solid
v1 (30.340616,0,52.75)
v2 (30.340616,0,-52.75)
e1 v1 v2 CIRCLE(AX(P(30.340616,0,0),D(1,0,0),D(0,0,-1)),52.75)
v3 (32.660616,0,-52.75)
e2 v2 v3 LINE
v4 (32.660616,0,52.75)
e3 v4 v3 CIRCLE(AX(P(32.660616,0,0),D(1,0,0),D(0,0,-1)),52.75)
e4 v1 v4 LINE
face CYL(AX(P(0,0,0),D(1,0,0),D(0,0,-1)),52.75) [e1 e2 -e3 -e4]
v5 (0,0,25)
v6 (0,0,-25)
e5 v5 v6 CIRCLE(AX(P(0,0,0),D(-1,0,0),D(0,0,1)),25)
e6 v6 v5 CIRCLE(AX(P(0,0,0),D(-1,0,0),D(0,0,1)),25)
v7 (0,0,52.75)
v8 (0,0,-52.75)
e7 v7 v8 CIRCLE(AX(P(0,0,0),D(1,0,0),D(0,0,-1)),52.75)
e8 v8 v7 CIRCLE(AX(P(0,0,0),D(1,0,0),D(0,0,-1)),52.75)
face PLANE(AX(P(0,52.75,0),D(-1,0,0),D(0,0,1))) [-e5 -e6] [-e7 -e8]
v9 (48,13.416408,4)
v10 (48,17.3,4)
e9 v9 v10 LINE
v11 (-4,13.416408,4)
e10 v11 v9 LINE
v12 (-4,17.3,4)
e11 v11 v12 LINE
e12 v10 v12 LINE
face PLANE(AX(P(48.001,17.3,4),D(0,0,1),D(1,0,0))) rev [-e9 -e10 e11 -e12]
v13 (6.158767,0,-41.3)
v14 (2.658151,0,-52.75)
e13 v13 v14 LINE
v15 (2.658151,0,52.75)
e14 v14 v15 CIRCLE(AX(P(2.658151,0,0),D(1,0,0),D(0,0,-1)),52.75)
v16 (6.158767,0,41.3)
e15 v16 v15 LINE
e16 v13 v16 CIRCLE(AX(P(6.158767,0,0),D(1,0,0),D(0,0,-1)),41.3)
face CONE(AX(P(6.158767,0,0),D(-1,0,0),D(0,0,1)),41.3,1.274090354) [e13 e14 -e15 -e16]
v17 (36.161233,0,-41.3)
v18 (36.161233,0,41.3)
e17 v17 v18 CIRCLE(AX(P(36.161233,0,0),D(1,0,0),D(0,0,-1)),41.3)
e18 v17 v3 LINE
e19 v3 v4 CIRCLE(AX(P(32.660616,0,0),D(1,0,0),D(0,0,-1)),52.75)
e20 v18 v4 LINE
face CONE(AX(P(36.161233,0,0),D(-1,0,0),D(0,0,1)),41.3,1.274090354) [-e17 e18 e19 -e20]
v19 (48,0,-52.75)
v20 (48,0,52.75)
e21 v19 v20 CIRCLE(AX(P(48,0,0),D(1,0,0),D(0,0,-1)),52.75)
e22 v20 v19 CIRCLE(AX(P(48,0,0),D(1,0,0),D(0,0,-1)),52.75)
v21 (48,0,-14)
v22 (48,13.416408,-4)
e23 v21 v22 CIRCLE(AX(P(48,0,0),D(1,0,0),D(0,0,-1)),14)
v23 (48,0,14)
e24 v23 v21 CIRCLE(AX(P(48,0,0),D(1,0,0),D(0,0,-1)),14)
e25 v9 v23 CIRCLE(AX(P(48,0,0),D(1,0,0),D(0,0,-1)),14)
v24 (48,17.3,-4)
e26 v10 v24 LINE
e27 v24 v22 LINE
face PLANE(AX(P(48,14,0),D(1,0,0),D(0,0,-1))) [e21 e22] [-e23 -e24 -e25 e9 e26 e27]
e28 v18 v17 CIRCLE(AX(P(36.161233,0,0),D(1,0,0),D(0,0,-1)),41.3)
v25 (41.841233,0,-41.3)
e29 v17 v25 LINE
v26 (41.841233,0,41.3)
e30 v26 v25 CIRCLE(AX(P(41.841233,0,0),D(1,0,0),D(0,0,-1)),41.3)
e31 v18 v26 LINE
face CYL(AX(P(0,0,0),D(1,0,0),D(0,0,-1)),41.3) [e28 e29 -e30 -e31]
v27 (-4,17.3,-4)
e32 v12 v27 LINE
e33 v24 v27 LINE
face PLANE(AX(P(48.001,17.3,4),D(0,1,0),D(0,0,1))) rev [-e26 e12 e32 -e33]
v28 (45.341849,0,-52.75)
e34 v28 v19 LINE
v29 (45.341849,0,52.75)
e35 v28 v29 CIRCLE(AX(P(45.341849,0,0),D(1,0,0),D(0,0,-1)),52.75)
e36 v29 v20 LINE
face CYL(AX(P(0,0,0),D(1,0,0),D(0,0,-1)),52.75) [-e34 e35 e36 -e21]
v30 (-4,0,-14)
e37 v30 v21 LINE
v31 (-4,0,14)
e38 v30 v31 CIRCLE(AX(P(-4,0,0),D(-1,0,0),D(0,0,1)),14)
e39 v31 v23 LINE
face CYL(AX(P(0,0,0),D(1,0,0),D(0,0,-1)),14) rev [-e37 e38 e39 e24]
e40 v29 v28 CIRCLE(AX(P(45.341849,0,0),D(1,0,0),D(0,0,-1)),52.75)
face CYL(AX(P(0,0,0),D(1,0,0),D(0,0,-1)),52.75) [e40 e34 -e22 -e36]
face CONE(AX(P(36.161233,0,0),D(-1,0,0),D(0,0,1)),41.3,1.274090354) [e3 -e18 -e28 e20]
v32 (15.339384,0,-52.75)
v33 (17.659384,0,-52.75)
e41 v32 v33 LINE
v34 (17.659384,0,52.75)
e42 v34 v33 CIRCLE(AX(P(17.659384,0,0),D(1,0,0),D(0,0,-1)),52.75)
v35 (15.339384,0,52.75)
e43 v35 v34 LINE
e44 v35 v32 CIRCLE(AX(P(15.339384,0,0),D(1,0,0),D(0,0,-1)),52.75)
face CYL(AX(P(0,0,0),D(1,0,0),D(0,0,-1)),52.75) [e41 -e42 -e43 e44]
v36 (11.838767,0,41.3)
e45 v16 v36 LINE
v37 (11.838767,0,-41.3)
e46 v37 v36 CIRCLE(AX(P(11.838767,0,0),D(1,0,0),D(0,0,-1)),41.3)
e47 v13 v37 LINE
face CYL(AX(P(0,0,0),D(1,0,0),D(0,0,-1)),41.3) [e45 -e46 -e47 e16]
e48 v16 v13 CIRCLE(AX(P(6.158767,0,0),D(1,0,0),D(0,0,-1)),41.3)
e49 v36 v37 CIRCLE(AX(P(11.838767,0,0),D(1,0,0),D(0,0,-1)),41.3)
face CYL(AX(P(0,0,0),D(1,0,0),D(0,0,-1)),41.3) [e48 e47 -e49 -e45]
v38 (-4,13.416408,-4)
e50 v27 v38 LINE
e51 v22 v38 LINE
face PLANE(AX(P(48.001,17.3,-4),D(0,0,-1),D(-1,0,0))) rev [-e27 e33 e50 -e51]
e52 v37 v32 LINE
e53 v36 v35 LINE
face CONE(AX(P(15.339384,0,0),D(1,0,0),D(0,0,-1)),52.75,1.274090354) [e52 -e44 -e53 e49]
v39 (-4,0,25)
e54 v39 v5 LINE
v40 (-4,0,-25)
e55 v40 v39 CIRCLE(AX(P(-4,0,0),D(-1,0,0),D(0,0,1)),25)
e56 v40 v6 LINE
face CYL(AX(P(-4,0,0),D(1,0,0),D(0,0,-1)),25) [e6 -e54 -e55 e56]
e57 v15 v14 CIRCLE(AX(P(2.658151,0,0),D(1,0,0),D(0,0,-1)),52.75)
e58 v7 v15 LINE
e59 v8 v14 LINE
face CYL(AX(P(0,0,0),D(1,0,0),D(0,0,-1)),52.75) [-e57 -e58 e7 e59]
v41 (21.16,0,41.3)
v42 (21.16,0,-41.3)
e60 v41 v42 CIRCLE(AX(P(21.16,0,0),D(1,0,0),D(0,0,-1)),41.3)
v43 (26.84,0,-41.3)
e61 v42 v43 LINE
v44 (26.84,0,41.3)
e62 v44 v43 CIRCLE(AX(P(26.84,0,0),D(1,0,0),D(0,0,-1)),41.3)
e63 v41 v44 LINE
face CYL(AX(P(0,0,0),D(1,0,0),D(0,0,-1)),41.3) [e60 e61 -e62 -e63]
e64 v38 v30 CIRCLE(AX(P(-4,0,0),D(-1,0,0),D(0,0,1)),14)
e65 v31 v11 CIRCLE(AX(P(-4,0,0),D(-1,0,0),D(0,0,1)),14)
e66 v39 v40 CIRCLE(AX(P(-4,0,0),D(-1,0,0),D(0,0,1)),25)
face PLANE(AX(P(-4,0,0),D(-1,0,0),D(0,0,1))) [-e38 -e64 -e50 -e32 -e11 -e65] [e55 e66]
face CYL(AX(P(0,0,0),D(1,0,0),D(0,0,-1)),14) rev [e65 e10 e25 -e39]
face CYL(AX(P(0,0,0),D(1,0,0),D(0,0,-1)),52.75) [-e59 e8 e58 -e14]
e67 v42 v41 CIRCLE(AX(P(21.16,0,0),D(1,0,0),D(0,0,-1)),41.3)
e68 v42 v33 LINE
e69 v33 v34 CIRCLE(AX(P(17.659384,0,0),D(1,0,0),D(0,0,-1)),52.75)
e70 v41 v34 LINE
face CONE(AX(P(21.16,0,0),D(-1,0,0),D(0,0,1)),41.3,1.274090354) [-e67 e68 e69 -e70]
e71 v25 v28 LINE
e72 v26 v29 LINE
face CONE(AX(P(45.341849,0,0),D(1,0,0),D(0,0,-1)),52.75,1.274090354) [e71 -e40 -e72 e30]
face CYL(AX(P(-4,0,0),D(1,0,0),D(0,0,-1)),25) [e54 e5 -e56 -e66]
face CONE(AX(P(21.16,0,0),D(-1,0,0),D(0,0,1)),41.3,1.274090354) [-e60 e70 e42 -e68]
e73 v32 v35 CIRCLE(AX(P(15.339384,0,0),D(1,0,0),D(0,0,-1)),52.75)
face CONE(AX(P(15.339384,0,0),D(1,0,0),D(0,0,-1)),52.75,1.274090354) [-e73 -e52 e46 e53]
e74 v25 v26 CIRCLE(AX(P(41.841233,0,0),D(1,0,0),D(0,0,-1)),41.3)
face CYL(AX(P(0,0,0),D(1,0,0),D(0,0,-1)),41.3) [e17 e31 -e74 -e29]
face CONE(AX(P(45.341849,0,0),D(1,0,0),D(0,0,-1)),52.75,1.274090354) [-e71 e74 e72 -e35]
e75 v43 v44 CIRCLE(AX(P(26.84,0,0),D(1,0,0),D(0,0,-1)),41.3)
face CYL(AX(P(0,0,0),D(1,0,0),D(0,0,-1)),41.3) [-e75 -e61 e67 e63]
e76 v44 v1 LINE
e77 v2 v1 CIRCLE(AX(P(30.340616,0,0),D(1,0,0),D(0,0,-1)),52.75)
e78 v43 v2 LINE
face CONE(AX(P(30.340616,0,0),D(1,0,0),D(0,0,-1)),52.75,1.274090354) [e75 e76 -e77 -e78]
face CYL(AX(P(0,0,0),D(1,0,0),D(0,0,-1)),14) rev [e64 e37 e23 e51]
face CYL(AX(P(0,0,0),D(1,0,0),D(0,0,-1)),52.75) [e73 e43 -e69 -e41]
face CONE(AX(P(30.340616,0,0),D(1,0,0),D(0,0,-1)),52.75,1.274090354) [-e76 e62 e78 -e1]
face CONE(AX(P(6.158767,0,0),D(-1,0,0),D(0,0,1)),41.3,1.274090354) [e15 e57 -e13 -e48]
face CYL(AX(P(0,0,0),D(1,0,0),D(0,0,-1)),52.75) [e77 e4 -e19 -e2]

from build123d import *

# Parameters (mm, degrees)
SKETCH8_R           = 25
SKETCH8_R_2         = 14
BOSS_EXTRUDE2_DEPTH = 4
CUT_EXTRUDE5_REACH  = 92.935
SKETCH9_W           = 8
SKETCH9_H           = 6.6


with BuildPart() as part:
    # Sketch1 → Revolve1 (revolve)
    with BuildSketch(Plane.XY, mode=Mode.PRIVATE) as revolve1_sk:
        Polygon((6.158767395, 41.3), (2.658151092, 52.75), (0, 52.75), (0, 14), (48, 14), (48, 52.75), (45.341848908, 52.75), (41.841232605, 41.3), (36.161232605, 41.3), (32.660616303, 52.75), (30.340616303, 52.75), (26.84, 41.3), (21.16, 41.3), (17.659383697, 52.75), (15.339383697, 52.75), (11.838767395, 41.3), align=None)
    revolve(revolve1_sk.sketch.rotate(Axis((0, 0, 0), (1, 0, 0)), 270), axis=Axis((0, 0, 0), (1, 0, 0)))

    # Sketch8 → Boss-Extrude2 (add)
    with BuildSketch(Plane.ZY):
        Circle(SKETCH8_R)
        with Locations(Location((0, 0, 0), (0, 0, 180))):
            Circle(SKETCH8_R_2, mode=Mode.SUBTRACT)
    extrude(amount=BOSS_EXTRUDE2_DEPTH)

    # Sketch9 → Cut-Extrude5 (cut, up to next)
    with BuildSketch(Plane.ZY.offset(4), mode=Mode.PRIVATE) as cut_extrude5_sk1:
        with Locations((0, 14)):
            Rectangle(SKETCH9_W, SKETCH9_H)
    cut_extrude5_tool1 = extrude(cut_extrude5_sk1.sketch, amount=-CUT_EXTRUDE5_REACH, mode=Mode.PRIVATE) & part.part
    add(cut_extrude5_tool1.solids().sort_by_distance((-4, 14, 0))[0], mode=Mode.SUBTRACT)


solid = part.part
